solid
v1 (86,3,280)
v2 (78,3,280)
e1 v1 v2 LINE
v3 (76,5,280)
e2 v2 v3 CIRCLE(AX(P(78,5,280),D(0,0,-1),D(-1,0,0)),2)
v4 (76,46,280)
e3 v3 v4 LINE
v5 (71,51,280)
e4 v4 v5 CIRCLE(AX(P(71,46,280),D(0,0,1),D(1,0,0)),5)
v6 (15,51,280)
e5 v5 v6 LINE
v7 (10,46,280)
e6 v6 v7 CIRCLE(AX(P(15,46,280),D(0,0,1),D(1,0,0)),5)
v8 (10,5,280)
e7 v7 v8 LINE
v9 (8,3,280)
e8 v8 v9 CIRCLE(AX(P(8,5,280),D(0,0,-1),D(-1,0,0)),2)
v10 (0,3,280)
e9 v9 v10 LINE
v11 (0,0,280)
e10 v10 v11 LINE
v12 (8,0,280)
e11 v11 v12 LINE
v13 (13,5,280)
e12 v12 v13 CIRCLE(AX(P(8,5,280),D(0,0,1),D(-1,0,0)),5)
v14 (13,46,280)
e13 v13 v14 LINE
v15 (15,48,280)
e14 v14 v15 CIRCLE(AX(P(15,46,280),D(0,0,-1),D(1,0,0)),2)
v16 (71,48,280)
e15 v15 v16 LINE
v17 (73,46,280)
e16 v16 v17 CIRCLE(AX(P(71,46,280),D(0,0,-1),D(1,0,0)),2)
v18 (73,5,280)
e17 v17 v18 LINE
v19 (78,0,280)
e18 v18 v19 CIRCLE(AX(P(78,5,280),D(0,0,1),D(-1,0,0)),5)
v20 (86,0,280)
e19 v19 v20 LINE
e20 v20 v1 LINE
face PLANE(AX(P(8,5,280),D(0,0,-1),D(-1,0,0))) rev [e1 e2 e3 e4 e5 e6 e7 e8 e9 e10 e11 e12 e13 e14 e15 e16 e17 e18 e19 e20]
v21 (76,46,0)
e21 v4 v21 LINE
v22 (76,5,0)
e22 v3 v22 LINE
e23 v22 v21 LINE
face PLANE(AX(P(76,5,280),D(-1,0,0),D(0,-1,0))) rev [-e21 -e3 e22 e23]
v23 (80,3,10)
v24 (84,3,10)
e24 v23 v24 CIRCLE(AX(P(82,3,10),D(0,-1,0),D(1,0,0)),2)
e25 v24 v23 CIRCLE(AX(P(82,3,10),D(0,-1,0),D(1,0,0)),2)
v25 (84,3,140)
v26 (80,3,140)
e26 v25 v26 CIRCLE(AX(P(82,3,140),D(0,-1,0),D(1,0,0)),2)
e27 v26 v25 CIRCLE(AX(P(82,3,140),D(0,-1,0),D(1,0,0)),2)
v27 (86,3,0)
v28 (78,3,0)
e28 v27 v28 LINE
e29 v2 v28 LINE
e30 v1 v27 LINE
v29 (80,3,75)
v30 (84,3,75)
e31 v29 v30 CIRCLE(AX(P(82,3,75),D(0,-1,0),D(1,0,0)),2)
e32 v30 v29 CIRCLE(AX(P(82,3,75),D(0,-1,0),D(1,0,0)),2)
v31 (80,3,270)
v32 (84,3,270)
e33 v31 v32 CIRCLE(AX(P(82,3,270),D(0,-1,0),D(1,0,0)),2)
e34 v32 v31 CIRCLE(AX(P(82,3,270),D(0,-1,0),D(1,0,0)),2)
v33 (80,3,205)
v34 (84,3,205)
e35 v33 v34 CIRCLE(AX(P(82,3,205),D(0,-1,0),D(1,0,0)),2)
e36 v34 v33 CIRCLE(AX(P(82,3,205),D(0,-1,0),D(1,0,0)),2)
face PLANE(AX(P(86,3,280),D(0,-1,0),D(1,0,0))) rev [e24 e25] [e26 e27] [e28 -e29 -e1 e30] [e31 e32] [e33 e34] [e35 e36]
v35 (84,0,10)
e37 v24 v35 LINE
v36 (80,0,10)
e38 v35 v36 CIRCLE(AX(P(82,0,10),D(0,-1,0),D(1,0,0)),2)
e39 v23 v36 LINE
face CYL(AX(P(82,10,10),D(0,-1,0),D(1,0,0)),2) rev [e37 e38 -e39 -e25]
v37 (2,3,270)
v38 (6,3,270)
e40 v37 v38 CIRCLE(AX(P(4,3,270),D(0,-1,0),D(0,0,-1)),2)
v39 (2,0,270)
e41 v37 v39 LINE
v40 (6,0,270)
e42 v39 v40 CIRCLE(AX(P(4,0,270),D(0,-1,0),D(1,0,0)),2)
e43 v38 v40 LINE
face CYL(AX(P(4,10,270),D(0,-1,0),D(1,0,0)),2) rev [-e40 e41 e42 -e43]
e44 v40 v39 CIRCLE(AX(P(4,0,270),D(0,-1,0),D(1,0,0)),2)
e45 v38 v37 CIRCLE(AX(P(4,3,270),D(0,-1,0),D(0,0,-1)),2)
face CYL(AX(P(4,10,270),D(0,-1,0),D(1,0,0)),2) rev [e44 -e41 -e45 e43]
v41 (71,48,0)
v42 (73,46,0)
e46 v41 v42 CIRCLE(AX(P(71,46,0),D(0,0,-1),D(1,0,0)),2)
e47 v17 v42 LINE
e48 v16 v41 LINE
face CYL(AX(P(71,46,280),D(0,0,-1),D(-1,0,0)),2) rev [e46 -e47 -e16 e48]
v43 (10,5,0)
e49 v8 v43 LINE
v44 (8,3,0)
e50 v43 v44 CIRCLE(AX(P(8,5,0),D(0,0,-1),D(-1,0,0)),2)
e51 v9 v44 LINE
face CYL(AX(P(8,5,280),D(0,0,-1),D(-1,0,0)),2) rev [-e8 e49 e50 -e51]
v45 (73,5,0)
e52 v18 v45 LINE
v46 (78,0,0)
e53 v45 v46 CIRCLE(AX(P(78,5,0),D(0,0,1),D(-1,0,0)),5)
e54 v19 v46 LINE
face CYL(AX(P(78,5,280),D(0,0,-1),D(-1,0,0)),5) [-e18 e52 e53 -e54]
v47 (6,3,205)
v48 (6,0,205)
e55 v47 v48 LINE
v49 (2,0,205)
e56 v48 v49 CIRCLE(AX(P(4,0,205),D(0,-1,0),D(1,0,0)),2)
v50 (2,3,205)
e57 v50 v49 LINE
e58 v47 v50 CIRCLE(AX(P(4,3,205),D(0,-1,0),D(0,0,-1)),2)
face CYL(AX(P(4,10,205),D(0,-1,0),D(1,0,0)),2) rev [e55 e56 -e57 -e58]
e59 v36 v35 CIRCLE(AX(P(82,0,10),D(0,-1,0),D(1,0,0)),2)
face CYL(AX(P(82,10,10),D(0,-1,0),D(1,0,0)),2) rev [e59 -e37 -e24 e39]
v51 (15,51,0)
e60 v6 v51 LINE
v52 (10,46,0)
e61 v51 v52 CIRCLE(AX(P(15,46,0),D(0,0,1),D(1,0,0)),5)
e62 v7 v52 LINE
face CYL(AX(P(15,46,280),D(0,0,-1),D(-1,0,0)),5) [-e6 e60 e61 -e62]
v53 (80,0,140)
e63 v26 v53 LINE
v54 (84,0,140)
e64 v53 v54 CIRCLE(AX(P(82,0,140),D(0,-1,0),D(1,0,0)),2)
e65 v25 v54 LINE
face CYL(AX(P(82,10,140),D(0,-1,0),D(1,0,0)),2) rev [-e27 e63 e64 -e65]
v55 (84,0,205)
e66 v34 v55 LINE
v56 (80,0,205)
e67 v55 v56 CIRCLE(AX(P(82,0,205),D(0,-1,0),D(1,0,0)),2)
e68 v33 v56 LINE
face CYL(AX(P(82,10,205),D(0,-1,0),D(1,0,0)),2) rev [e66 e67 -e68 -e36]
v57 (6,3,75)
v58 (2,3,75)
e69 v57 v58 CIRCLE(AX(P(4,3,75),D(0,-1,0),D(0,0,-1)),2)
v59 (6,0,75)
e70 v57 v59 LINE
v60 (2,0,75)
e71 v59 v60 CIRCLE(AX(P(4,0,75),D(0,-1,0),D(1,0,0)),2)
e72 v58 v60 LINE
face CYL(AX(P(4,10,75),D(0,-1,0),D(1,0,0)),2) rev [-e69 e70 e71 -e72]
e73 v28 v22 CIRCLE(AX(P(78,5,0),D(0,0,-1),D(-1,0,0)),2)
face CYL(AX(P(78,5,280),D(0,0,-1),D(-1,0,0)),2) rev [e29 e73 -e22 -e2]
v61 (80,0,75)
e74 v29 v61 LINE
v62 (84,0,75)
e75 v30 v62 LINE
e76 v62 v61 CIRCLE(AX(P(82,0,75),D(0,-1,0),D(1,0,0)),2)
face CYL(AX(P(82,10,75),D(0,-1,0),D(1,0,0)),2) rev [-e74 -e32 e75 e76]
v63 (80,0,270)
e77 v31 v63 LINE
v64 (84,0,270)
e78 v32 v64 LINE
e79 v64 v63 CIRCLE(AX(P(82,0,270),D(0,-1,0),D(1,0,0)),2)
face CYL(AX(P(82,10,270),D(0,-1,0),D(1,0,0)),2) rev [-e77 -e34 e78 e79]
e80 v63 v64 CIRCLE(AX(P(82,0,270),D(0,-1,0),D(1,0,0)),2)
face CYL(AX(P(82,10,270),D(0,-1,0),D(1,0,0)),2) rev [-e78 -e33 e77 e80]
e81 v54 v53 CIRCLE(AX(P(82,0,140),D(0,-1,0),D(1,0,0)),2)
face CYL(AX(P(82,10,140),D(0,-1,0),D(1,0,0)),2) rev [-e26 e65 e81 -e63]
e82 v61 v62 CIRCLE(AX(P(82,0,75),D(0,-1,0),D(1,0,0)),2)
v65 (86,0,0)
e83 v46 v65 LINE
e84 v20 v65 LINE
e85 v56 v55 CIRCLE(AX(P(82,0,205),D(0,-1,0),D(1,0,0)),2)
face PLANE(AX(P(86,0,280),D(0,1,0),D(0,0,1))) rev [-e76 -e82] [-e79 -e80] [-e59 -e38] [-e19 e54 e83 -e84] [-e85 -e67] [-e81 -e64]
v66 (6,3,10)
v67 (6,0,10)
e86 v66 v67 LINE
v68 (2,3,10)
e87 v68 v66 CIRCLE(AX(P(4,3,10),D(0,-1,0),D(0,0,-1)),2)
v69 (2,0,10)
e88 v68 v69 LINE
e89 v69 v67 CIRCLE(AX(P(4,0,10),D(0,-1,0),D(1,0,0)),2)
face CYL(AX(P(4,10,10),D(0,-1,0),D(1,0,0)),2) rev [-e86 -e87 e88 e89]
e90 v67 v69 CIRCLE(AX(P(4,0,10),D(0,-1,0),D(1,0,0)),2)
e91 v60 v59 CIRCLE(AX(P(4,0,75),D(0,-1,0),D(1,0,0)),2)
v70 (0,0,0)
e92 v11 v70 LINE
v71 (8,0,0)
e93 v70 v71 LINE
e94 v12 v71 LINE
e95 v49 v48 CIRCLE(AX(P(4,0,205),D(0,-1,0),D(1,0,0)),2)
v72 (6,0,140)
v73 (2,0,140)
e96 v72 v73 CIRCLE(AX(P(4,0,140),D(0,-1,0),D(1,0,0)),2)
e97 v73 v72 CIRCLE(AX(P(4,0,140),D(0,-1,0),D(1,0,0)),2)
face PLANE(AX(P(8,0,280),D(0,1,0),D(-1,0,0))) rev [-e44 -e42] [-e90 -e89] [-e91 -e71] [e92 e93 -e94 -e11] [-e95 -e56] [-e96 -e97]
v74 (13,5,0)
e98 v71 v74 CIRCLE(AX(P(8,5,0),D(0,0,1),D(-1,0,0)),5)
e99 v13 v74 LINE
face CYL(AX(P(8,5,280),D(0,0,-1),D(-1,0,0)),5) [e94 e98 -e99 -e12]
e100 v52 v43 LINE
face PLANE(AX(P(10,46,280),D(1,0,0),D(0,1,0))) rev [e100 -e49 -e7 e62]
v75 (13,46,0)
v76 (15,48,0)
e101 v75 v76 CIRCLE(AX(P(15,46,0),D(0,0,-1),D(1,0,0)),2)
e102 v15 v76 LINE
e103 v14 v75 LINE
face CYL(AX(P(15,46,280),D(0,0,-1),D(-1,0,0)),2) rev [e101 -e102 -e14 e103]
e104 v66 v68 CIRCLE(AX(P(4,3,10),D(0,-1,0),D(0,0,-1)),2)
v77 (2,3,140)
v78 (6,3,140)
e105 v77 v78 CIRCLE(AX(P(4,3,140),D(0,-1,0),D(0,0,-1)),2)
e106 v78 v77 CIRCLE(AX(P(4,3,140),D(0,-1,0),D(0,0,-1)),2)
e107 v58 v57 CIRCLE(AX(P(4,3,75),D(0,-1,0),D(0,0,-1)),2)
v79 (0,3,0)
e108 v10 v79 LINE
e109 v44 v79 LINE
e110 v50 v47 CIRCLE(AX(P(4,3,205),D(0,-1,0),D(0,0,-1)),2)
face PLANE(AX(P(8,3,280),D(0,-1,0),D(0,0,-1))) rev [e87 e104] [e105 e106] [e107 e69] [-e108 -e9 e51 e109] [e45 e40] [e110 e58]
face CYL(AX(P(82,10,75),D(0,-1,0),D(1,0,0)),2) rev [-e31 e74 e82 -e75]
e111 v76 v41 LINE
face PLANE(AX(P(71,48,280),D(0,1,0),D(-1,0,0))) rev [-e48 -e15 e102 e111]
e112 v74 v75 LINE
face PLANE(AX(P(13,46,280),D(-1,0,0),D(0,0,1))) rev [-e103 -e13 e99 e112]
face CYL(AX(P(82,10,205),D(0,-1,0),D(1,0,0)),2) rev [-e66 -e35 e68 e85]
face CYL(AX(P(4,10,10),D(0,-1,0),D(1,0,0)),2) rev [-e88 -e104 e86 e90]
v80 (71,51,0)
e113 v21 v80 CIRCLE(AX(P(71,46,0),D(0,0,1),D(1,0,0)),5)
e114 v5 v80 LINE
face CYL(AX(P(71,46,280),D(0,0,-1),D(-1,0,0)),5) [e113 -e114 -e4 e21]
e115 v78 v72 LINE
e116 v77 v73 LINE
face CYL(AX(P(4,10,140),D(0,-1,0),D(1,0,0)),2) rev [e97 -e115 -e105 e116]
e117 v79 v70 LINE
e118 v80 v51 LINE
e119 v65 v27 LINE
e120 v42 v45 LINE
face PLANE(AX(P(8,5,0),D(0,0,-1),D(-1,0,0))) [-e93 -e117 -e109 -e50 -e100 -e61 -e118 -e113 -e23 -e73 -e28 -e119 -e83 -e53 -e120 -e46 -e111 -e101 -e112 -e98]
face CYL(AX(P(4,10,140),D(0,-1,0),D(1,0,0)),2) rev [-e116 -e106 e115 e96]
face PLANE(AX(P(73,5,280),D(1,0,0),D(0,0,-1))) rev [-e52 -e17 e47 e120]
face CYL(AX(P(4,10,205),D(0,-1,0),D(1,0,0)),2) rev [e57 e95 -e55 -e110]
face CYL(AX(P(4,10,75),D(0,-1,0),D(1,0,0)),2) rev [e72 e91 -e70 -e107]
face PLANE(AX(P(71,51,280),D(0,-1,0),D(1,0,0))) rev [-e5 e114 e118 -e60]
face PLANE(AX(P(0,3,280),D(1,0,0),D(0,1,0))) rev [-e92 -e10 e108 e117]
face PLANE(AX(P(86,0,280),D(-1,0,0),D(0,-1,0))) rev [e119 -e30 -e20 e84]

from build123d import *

# Parameters (mm, degrees)
BOSS_EXTRUDE1_DEPTH = 280
SKETCH7_R           = 2
CUT_EXTRUDE3_DEPTH  = 10
LPATTERN1_COUNT     = 5
LPATTERN1_PITCH     = 65


with BuildPart() as part:
    # Sketch1 → Boss-Extrude1 (new body)
    with BuildSketch(Plane.XY):
        with BuildLine():
            Line((86, 0), (86, 3))
            Line((86, 3), (78, 3))
            ThreePointArc((78, 3), (76.585786438, 3.585786438), (76, 5))
            Line((76, 5), (76, 46))
            ThreePointArc((76, 46), (74.535533906, 49.535533906), (71, 51))
            Line((71, 51), (15, 51))
            ThreePointArc((15, 51), (11.464466094, 49.535533906), (10, 46))
            Line((10, 46), (10, 5))
            ThreePointArc((10, 5), (9.414213562, 3.585786438), (8, 3))
            Line((8, 3), (0, 3))
            Line((0, 3), (0, 0))
            Line((0, 0), (8, 0))
            ThreePointArc((8, 0), (11.535533906, 1.464466094), (13, 5))
            Line((13, 5), (13, 46))
            ThreePointArc((13, 46), (13.585786438, 47.414213562), (15, 48))
            Line((15, 48), (71, 48))
            ThreePointArc((71, 48), (72.414213562, 47.414213562), (73, 46))
            Line((73, 46), (73, 5))
            ThreePointArc((73, 5), (74.464466094, 1.464466094), (78, 0))
            Line((78, 0), (86, 0))
        make_face()
    extrude(amount=BOSS_EXTRUDE1_DEPTH)

    # Sketch7 → Cut-Extrude3 (cut)
    with BuildSketch(Plane(origin=(0, 0, 0), x_dir=(-1, 0, 0), z_dir=(0, -1, 0))):
        with Locations(Location((-4, -270, 0), (0, 0, 180))):
            Circle(SKETCH7_R)
        with Locations(Location((-82, -270, 0), (0, 0, 180))):
            Circle(SKETCH7_R)
    cut_extrude3 = extrude(amount=-CUT_EXTRUDE3_DEPTH, mode=Mode.SUBTRACT)

    # LPattern1: Cut-Extrude3 ×5
    with Locations(*[(0, 0, -i * LPATTERN1_PITCH) for i in range(1, LPATTERN1_COUNT)]):
        add(cut_extrude3, mode=Mode.SUBTRACT)


solid = part.part
